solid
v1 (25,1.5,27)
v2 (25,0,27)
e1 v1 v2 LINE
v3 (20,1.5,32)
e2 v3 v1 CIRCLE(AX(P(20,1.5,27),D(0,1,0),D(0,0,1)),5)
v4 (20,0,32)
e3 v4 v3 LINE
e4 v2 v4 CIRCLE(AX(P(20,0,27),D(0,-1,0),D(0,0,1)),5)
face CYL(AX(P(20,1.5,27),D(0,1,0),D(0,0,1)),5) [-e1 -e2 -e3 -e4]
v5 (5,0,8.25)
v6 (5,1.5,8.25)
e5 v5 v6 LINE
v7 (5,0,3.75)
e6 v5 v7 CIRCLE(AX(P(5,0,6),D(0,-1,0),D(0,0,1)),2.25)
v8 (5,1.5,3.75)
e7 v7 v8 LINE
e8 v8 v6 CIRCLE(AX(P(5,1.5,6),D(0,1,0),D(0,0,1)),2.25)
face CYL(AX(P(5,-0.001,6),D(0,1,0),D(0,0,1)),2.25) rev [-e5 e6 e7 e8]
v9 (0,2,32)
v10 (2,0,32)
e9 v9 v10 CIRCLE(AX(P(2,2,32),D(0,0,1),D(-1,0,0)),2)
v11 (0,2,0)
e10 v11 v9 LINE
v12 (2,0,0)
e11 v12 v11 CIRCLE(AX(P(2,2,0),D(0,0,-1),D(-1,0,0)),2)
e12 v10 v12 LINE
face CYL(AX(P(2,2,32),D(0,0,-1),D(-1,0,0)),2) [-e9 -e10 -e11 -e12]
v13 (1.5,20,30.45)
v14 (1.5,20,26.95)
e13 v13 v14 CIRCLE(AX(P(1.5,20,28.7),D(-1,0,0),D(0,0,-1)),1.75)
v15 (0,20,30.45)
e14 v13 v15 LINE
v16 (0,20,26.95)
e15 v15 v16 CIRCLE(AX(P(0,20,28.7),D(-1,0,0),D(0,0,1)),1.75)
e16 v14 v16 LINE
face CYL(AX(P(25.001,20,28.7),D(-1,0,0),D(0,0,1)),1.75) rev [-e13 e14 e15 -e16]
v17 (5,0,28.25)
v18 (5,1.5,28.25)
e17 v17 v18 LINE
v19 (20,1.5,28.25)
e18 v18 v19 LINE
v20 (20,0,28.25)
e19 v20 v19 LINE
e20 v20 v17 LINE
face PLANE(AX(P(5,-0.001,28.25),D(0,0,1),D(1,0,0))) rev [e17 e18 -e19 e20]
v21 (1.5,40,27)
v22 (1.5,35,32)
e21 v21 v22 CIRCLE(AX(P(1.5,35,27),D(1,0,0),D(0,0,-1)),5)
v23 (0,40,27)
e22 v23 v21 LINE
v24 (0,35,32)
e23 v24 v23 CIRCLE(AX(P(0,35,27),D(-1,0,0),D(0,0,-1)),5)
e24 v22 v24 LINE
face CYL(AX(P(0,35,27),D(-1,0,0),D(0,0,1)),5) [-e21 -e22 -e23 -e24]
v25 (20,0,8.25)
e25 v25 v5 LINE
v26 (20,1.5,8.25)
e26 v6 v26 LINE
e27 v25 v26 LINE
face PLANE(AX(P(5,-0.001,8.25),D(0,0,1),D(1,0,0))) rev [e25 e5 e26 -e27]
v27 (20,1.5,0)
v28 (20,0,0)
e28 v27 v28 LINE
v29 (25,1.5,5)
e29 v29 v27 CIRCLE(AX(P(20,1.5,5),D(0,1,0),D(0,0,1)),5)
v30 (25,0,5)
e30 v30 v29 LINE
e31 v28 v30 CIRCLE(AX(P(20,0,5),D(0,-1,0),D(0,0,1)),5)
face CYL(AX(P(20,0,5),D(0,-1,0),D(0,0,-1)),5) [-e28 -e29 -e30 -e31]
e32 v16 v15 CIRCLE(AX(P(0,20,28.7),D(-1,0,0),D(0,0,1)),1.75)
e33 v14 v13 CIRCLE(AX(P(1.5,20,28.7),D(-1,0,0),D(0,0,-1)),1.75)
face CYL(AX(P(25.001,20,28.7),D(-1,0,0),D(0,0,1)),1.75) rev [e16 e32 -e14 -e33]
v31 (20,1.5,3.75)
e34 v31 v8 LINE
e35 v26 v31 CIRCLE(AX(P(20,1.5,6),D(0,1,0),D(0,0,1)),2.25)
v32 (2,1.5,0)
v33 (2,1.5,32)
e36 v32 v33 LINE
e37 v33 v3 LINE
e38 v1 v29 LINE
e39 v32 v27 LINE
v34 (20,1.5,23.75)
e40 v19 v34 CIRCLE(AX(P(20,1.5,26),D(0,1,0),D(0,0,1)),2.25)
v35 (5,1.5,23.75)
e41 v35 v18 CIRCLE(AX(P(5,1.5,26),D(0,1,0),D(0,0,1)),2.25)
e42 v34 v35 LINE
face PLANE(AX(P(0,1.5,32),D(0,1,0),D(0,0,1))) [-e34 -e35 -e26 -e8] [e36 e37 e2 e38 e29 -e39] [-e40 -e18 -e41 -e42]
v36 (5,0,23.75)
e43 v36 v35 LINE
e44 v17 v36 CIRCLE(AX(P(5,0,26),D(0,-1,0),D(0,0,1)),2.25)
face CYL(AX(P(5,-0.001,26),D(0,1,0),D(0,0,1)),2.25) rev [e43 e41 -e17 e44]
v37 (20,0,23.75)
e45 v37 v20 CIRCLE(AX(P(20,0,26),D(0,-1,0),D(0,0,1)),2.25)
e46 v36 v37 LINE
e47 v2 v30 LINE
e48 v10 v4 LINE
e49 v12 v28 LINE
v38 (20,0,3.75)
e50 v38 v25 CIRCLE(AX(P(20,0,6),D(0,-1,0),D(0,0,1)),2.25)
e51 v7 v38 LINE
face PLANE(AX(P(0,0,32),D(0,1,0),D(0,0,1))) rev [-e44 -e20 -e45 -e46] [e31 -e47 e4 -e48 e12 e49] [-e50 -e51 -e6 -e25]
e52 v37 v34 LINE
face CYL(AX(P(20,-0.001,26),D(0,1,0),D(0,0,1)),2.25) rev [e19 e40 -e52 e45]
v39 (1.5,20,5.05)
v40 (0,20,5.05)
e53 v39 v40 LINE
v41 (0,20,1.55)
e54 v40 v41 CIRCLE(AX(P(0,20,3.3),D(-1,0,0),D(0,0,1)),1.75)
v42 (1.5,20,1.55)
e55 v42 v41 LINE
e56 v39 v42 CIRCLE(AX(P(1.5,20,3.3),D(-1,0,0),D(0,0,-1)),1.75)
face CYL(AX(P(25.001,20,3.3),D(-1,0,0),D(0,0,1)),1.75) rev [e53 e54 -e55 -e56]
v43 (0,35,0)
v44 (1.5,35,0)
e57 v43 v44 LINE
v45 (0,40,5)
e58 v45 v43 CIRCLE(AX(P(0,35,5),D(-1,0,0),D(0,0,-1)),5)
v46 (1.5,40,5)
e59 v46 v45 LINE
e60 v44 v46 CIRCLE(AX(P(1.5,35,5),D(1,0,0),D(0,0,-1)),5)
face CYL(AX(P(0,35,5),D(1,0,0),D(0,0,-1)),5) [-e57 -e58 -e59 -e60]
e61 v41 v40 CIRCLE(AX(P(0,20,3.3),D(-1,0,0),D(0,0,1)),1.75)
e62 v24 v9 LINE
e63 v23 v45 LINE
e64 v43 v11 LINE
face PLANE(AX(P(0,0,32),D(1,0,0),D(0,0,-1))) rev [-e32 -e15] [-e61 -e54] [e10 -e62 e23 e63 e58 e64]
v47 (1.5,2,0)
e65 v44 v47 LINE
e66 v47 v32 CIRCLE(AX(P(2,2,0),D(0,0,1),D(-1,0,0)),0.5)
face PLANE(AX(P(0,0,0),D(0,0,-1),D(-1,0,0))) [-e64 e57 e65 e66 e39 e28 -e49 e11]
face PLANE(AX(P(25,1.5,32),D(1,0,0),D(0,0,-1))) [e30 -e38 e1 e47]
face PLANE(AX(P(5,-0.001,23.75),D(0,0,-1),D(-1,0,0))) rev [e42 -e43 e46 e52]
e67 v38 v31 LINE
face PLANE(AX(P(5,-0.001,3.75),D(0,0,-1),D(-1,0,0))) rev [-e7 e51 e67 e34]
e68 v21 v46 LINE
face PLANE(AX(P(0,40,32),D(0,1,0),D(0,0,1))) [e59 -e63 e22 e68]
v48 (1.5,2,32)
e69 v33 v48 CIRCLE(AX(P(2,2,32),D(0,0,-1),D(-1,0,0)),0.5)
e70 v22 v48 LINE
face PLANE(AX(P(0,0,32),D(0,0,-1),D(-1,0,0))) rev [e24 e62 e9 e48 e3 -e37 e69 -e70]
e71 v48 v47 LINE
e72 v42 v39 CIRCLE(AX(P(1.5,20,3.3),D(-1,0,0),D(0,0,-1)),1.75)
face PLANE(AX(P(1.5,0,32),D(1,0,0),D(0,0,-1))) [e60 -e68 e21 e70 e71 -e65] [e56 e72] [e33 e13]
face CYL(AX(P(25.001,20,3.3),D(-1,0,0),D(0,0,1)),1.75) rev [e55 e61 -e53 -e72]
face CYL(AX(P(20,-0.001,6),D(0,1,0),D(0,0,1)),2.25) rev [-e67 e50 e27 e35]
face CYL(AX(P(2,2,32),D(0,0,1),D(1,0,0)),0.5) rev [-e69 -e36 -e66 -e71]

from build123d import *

# Parameters (mm, degrees)
EXTRUDE_1_DEPTH     = 32
FILLET_1_R          = 0.5
FILLET_2_R          = 2
FILLET_3_R          = 5
CUT_EXTRUDE_1_REACH = 59
SKETCH_2_R          = 1.75
CUT_EXTRUDE_2_REACH = 57.958


with BuildPart() as part:
    # 草图1 → 拉伸-薄壁1 (new body)
    with BuildSketch(Plane.XY):
        Polygon((25, 0), (0, 0), (0, 40), (1.5, 40), (1.5, 1.5), (25, 1.5), align=None)
    extrude(amount=EXTRUDE_1_DEPTH)

    # 圆角1
    fillet_1_edges = [part.edges().sort_by_distance(p)[0] for p in [
        (1.5, 1.5, 16),
    ]]
    fillet(fillet_1_edges, radius=FILLET_1_R)

    # 圆角2
    fillet_2_edges = [part.edges().sort_by_distance(p)[0] for p in [
        (0, 0, 16),
    ]]
    fillet(fillet_2_edges, radius=FILLET_2_R)

    # 圆角3
    fillet_3_edges = [part.edges().sort_by_distance(p)[0] for p in [
        (0.75, 40, 32),
        (0.75, 40, 0),
        (25, 0.75, 0),
        (25, 0.75, 32),
    ]]
    fillet(fillet_3_edges, radius=FILLET_3_R)

    # 草图2 → 切除-拉伸1 (cut, up to next)
    with BuildSketch(Plane.ZY, mode=Mode.PRIVATE) as cut_extrude_1_sk1:
        with Locations((3.3, 20)):
            Circle(SKETCH_2_R)
    cut_extrude_1_tool1 = extrude(cut_extrude_1_sk1.sketch, amount=-CUT_EXTRUDE_1_REACH, mode=Mode.PRIVATE) & part.part
    # 草图2 → 切除-拉伸1 (cut, up to next)
    with BuildSketch(Plane.ZY, mode=Mode.PRIVATE) as cut_extrude_1_sk2:
        with Locations((28.7, 20)):
            Circle(SKETCH_2_R)
    cut_extrude_1_tool2 = extrude(cut_extrude_1_sk2.sketch, amount=-CUT_EXTRUDE_1_REACH, mode=Mode.PRIVATE) & part.part
    add(cut_extrude_1_tool1.solids().sort_by_distance((0, 20, 3.3))[0], mode=Mode.SUBTRACT)
    add(cut_extrude_1_tool2.solids().sort_by_distance((0, 20, 28.7))[0], mode=Mode.SUBTRACT)

    # 草图3 → 切除-拉伸2 (cut, up to next)
    with BuildSketch(Plane(origin=(0, 1.5, 0), x_dir=(1, 0, 0), z_dir=(0, 1, 0)), mode=Mode.PRIVATE) as cut_extrude_2_sk1:
        with BuildLine():
            Line((5, -3.75), (20, -3.75))
            ThreePointArc((20, -3.75), (22.25, -6), (20, -8.25))
            Line((20, -8.25), (5, -8.25))
            ThreePointArc((5, -8.25), (2.75, -6), (5, -3.75))
        make_face()
    cut_extrude_2_tool1 = extrude(cut_extrude_2_sk1.sketch, amount=-CUT_EXTRUDE_2_REACH, mode=Mode.PRIVATE) & part.part
    # 草图3 → 切除-拉伸2 (cut, up to next)
    with BuildSketch(Plane(origin=(0, 1.5, 0), x_dir=(1, 0, 0), z_dir=(0, 1, 0)), mode=Mode.PRIVATE) as cut_extrude_2_sk2:
        with BuildLine():
            Line((5, -23.75), (20, -23.75))
            ThreePointArc((20, -23.75), (22.25, -26), (20, -28.25))
            Line((20, -28.25), (5, -28.25))
            ThreePointArc((5, -28.25), (2.75, -26), (5, -23.75))
        make_face()
    cut_extrude_2_tool2 = extrude(cut_extrude_2_sk2.sketch, amount=-CUT_EXTRUDE_2_REACH, mode=Mode.PRIVATE) & part.part
    add(cut_extrude_2_tool1.solids().sort_by_distance((12.5, 1.5, 6))[0], mode=Mode.SUBTRACT)
    add(cut_extrude_2_tool2.solids().sort_by_distance((12.5, 1.5, 26))[0], mode=Mode.SUBTRACT)


solid = part.part
